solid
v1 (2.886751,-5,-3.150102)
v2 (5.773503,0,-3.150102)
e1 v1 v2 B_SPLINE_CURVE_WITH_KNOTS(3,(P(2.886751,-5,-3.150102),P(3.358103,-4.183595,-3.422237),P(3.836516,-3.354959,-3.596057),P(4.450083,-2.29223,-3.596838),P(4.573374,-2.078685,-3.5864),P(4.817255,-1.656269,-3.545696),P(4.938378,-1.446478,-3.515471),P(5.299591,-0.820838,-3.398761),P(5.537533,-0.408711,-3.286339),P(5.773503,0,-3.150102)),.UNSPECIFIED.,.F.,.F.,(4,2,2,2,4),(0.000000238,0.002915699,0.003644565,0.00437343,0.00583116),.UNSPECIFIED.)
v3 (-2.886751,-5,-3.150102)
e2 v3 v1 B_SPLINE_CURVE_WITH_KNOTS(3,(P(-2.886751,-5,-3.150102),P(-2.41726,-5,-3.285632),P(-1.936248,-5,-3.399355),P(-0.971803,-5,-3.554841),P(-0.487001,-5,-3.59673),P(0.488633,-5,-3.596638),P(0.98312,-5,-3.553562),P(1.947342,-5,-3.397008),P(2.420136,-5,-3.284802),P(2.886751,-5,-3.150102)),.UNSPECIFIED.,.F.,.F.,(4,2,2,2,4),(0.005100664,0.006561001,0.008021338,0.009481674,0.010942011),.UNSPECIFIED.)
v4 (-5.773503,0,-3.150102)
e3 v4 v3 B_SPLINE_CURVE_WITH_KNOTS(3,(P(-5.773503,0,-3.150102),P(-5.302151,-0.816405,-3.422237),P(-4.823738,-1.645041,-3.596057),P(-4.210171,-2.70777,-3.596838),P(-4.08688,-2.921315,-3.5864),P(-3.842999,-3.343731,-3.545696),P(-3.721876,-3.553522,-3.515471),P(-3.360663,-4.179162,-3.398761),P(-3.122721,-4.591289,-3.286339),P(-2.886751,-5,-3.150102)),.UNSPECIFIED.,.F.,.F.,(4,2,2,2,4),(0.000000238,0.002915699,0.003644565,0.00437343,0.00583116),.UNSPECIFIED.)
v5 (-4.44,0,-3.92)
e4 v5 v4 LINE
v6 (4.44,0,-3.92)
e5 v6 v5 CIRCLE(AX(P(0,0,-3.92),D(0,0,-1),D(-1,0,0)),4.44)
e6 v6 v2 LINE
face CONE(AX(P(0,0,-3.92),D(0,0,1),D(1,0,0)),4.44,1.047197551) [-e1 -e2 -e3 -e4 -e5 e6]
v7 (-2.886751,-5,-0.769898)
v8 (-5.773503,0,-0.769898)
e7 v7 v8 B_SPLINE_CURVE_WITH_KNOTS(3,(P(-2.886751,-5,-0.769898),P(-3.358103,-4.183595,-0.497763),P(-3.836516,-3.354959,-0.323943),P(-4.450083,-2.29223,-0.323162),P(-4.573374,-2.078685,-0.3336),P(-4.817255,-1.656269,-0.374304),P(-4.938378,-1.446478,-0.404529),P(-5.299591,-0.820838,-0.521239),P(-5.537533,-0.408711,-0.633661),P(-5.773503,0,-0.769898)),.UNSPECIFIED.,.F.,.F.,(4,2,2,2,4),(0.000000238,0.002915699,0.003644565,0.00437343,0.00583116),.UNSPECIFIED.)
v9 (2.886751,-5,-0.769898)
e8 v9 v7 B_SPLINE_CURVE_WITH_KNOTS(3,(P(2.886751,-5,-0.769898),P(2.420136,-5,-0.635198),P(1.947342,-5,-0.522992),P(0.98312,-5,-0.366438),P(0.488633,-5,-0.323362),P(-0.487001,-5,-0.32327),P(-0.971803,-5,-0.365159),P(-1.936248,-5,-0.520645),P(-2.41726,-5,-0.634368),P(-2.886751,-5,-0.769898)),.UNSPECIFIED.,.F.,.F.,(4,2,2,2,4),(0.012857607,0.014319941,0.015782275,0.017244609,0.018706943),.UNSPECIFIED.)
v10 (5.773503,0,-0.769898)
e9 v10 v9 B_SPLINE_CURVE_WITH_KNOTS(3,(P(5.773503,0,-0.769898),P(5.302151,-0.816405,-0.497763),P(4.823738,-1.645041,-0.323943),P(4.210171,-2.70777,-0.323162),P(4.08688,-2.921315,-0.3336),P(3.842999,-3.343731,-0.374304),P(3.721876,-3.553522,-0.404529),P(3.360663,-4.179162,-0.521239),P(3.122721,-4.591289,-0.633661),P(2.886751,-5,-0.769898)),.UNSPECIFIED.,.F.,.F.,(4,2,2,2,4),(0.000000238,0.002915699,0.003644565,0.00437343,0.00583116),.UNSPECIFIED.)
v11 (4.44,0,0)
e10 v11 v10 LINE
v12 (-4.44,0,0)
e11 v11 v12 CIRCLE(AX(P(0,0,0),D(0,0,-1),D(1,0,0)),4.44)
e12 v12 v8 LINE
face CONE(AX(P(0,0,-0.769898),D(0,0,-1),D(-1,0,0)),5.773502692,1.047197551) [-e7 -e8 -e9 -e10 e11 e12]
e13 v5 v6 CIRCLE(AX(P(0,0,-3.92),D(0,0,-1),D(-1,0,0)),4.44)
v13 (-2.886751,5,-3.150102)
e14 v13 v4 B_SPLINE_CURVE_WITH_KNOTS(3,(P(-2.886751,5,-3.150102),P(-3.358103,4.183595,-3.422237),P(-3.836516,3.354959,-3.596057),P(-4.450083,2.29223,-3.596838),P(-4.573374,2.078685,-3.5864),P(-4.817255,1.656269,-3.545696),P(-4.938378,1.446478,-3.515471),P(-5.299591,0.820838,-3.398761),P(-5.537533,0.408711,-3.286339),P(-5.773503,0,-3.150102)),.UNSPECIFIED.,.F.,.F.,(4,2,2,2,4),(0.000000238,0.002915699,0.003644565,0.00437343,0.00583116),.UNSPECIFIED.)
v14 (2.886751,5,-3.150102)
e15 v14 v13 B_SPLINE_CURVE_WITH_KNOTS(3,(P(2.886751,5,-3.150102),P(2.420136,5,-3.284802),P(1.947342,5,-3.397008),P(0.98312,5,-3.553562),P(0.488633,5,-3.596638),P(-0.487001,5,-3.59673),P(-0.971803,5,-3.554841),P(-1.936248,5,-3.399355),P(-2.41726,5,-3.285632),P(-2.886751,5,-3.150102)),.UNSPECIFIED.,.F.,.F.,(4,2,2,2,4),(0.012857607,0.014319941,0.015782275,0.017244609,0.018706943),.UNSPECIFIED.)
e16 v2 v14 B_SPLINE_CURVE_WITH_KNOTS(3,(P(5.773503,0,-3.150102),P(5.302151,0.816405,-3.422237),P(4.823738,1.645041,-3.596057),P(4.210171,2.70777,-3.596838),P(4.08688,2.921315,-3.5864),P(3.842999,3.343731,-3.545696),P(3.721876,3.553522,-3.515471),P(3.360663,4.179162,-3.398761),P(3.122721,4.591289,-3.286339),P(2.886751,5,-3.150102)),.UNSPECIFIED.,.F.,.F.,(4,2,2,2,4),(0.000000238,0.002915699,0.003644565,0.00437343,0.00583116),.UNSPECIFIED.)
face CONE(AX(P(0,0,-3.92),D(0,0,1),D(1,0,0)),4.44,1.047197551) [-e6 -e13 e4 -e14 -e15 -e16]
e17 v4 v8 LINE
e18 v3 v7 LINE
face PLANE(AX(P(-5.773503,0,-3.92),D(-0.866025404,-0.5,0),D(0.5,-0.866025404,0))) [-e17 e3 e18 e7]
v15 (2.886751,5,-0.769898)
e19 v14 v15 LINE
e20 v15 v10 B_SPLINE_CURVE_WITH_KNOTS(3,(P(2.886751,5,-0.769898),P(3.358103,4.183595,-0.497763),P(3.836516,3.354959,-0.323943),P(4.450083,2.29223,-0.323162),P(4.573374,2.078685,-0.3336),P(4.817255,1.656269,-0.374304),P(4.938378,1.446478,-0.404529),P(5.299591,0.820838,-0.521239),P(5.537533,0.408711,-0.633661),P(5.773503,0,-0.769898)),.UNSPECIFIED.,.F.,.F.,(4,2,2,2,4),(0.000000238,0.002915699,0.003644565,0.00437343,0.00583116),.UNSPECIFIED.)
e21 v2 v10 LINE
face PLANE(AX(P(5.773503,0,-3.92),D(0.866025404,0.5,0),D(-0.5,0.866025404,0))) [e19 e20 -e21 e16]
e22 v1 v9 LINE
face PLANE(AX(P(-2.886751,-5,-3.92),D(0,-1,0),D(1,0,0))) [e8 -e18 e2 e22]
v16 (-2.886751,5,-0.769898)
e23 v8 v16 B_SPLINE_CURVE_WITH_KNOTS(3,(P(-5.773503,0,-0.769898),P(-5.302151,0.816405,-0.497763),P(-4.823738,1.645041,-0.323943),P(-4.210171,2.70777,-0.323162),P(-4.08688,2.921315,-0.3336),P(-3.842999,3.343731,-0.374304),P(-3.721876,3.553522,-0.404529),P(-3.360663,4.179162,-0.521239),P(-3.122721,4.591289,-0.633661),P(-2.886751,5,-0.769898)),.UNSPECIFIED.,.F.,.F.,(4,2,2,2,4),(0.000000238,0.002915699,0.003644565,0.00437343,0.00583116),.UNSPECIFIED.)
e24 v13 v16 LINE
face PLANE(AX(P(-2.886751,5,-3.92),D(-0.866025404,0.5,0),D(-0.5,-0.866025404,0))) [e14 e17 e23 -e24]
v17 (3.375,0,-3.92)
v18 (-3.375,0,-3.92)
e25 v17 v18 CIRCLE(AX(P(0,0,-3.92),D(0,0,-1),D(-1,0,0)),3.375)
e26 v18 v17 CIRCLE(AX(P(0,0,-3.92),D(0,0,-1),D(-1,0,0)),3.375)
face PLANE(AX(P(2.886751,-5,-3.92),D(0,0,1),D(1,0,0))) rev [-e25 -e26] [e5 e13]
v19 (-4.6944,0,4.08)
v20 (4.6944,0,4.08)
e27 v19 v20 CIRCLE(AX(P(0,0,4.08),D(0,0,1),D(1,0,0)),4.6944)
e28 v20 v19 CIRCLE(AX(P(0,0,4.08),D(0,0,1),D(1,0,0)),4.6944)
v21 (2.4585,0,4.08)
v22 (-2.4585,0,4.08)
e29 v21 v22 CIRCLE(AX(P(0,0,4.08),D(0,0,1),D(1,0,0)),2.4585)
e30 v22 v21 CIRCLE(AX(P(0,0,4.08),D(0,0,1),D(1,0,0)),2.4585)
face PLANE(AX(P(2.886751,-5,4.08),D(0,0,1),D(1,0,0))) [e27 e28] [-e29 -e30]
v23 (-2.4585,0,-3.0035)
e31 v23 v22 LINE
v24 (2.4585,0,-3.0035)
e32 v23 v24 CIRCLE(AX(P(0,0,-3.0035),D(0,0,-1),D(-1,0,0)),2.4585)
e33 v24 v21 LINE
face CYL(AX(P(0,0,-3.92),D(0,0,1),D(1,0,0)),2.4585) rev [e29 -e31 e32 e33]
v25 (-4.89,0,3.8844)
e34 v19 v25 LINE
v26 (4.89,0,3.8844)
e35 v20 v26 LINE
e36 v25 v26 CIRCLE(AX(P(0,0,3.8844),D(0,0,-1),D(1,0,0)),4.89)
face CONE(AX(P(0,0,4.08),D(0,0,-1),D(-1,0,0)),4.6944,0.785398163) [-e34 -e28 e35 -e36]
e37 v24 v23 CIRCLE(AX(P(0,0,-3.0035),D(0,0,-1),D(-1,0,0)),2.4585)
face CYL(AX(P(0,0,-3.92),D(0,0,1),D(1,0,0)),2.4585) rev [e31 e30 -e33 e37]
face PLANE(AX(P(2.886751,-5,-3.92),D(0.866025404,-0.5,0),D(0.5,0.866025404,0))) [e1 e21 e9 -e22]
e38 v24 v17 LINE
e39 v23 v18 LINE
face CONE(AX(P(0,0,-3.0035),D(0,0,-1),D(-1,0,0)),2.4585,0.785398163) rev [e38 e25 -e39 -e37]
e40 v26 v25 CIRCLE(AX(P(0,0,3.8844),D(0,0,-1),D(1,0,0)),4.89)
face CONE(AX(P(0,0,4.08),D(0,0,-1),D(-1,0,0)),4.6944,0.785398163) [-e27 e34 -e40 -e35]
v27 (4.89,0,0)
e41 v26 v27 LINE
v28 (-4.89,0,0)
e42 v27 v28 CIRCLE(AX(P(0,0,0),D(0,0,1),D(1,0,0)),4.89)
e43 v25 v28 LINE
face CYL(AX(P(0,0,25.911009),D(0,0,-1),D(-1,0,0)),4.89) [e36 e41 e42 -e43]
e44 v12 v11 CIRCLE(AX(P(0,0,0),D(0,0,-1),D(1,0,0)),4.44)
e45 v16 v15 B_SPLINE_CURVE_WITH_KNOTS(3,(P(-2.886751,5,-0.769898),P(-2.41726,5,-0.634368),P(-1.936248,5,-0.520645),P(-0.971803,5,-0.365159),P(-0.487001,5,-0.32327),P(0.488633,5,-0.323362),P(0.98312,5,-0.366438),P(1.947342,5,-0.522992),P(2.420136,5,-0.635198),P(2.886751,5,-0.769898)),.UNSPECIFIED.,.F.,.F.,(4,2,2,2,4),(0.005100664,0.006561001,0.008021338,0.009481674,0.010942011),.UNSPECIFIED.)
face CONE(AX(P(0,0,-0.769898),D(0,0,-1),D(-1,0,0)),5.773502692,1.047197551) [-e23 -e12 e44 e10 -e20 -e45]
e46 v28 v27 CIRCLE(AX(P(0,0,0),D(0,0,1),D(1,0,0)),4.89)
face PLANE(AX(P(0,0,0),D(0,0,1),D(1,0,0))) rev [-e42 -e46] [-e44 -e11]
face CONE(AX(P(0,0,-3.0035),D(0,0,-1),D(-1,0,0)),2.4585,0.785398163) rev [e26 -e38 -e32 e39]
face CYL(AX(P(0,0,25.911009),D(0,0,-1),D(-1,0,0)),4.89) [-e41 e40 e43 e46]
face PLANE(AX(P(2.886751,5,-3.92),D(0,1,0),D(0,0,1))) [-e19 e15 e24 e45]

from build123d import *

# Parameters (mm, degrees)
SKETCH1_R      = 2.4585
BASENUT_DEPTH  = 3.92
EXTRUDE1_START = 4.08
SKETCH2_R      = 4.89
SKETCH2_R_2    = 2.4585
EXTRUDE1_DEPTH = 4.08
CHAMFER1_SIZE  = 0.1956


with BuildPart() as part:
    # Sketch1 → BaseNut (new body)
    with BuildSketch(Plane.XY):
        Polygon((2.886751346, -5), (5.773502692, 0), (2.886751346, 5), (-2.886751346, 5), (-5.773502692, 0), (-2.886751346, -5), align=None)
        Circle(SKETCH1_R, mode=Mode.SUBTRACT)
    extrude(amount=-BASENUT_DEPTH)

    # Sketch3 → Double-Chamfer (revolve, cut)
    with BuildSketch(Plane(origin=(0, 0, 0), x_dir=(1, 0, 0), z_dir=(0, 1, 0)), mode=Mode.PRIVATE) as double_chamfer_sk:
        Polygon((4.44, 3.92), (5.773502692, 3.92), (5.773502692, 3.150101862), align=None)
        Polygon((5.773502692, 0.769898138), (4.44, 0), (5.773502692, 0), align=None)
    revolve(double_chamfer_sk.sketch.rotate(Axis((0, 0, -16.31077227), (0, 0, 1)), 179.999999973), axis=Axis((0, 0, -16.31077227), (0, 0, 1)), mode=Mode.SUBTRACT)

    # Sketch2 → Extrude1 (add)
    with BuildSketch(Plane(origin=(20.087129569, -4.281493882, 0), x_dir=(1, 0, 0), z_dir=(0, 0, 1)).offset(EXTRUDE1_START)):
        with Locations((-20.087129569, 4.281493882)):
            Circle(SKETCH2_R)
        with Locations((-20.087129569, 4.281493882)):
            Circle(SKETCH2_R_2, mode=Mode.SUBTRACT)
    extrude(amount=-EXTRUDE1_DEPTH)

    # Sketch5 → EndChamfer (revolve, cut)
    with BuildSketch(Plane(origin=(0, 0, 0), x_dir=(1, 0, 0), z_dir=(0, 1, 0))):
        Polygon((2.4585, 3.92), (3.375, 3.92), (2.4585, 3.0035), align=None)
    revolve(axis=Axis((0, 0, -16.800797033), (0, 0, 1)), mode=Mode.SUBTRACT)

    # Chamfer1
    chamfer1_edges = [part.edges().sort_by_distance(p)[0] for p in [
        (-4.89, 0, 4.08),
    ]]
    chamfer(chamfer1_edges, length=CHAMFER1_SIZE)


solid = part.part
